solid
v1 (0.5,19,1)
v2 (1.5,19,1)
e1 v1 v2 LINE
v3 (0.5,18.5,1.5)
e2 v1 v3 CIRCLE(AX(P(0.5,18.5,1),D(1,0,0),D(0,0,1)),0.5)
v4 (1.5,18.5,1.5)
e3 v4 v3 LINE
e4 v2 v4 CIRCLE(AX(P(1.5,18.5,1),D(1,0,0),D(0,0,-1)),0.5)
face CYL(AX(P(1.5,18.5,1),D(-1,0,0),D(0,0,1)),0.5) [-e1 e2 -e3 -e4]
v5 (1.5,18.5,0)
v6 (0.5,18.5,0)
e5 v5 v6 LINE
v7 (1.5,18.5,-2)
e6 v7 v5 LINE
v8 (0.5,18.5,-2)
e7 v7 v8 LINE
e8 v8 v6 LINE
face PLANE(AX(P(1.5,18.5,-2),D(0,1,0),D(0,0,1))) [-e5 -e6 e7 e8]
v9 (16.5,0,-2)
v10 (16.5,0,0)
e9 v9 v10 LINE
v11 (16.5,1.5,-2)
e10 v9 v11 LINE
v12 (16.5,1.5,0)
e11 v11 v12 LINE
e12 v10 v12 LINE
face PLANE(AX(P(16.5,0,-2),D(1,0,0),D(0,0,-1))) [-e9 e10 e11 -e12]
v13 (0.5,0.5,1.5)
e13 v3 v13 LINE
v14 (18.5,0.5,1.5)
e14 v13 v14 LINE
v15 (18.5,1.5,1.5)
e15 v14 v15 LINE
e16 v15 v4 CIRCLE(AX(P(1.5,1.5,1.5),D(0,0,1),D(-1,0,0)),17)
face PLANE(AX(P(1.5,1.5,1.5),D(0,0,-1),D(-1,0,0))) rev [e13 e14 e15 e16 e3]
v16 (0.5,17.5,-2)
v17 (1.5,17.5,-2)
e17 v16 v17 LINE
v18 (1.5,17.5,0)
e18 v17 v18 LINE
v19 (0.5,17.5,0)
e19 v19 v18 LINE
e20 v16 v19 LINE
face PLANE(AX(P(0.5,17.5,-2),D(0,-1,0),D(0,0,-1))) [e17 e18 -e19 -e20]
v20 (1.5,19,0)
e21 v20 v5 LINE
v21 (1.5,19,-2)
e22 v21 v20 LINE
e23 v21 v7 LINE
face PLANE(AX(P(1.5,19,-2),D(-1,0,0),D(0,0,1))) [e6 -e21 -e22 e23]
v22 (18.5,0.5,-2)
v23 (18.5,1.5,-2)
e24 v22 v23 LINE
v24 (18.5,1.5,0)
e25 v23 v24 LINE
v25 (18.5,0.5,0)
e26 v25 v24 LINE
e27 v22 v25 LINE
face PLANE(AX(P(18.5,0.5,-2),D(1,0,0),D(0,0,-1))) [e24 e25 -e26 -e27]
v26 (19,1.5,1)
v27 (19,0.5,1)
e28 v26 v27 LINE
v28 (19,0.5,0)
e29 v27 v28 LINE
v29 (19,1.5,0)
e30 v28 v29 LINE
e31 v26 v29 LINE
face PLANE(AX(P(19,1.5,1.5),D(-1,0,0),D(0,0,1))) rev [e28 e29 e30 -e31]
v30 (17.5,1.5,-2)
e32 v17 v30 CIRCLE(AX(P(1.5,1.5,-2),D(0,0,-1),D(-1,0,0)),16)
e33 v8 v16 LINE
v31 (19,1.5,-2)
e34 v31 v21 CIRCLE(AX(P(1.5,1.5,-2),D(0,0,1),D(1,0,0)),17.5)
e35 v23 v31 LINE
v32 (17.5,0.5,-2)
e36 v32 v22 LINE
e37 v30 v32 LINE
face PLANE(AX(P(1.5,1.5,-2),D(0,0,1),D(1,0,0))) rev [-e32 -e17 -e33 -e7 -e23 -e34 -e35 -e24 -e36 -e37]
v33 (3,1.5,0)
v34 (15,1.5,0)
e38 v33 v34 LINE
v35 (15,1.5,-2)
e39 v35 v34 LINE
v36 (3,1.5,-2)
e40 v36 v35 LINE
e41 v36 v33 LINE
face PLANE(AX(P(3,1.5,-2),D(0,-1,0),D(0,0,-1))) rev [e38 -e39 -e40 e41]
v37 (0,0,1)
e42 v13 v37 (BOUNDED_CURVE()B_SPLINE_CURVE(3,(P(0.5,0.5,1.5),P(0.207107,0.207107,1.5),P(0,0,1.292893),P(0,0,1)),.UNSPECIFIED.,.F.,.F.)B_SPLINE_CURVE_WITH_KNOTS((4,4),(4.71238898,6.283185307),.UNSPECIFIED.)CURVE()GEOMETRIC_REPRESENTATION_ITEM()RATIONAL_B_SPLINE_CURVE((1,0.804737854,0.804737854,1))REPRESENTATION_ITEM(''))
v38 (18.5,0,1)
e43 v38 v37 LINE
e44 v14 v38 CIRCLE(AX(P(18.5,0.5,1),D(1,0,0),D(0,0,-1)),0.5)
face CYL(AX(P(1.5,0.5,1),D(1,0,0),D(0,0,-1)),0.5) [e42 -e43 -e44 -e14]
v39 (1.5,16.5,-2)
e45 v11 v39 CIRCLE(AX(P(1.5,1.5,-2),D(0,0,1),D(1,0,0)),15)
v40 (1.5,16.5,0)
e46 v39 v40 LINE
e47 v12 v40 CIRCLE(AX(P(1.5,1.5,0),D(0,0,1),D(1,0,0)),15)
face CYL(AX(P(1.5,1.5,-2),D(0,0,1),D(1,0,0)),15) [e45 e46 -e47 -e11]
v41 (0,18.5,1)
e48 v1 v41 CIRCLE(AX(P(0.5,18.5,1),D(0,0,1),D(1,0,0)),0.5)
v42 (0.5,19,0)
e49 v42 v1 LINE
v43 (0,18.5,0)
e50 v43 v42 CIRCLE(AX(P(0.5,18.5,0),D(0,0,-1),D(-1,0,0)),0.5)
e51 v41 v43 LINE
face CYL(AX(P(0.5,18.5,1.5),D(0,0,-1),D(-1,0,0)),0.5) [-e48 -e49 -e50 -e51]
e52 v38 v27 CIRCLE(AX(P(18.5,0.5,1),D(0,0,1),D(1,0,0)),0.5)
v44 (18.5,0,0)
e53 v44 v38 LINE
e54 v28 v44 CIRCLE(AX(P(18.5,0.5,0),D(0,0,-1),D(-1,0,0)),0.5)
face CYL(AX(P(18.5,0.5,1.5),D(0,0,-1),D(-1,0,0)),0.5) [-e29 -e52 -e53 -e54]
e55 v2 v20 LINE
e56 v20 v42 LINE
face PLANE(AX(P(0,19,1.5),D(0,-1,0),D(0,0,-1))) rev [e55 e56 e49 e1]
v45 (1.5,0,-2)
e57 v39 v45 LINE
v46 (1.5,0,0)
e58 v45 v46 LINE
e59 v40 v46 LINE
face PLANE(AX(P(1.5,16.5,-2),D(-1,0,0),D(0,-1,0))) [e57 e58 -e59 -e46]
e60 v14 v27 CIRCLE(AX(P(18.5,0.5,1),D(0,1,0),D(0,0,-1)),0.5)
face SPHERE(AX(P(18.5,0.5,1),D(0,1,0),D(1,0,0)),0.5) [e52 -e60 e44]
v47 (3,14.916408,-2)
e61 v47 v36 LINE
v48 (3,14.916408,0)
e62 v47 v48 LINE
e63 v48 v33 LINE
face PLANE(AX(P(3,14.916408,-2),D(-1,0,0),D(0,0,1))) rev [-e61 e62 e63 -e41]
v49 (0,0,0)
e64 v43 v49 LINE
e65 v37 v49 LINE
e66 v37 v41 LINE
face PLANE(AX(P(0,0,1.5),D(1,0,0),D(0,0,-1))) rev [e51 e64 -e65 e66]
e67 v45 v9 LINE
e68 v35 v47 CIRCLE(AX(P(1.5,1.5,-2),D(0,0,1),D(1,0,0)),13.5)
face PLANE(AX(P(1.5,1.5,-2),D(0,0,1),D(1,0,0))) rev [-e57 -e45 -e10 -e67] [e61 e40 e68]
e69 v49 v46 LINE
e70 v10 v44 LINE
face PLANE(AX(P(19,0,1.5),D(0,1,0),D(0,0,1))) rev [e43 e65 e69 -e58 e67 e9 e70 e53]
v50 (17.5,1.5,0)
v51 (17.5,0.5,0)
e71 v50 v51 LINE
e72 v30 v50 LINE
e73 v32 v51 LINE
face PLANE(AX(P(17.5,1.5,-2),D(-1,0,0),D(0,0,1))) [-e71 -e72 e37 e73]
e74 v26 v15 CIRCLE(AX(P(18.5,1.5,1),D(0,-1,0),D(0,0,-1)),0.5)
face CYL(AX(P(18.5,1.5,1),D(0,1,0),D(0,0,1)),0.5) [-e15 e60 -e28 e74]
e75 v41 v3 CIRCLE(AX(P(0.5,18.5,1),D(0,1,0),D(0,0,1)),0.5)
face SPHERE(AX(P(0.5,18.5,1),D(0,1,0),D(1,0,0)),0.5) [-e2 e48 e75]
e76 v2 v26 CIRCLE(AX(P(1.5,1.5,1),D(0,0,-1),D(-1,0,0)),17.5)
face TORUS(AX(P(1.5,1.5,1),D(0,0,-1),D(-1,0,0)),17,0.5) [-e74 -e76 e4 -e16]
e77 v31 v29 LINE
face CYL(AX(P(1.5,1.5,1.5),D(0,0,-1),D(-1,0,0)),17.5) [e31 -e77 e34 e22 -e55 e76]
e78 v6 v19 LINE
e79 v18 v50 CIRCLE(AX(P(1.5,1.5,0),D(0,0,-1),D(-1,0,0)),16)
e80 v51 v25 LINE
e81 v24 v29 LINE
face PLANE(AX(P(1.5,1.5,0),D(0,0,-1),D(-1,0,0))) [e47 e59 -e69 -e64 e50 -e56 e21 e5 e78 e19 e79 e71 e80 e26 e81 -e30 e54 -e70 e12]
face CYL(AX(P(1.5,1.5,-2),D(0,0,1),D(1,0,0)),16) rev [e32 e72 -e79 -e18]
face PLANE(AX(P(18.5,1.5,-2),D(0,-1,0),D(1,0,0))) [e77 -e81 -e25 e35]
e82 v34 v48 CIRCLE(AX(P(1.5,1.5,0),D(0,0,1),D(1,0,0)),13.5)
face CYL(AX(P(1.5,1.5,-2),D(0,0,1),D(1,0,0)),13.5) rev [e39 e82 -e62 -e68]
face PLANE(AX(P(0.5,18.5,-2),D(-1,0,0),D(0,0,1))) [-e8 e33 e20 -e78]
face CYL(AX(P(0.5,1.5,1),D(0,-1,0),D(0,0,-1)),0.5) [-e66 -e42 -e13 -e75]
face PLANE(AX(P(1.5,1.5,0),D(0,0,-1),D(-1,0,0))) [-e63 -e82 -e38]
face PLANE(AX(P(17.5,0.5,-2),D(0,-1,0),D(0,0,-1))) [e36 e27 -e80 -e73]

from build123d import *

# Parameters (mm, degrees)
BOSS_EXTRUDE1_DEPTH = 1.5
BOSS_EXTRUDE3_START = -2
BOSS_EXTRUDE3_DEPTH = 2
FILETE1_R           = 0.5


with BuildPart() as part:
    # Sketch1 → Boss-Extrude1 (new body)
    with BuildSketch(Plane.XY):
        with BuildLine():
            Line((0, 0), (0, 19))
            Line((0, 19), (1.5, 19))
            ThreePointArc((1.5, 19), (13.874368671, 13.874368671), (19, 1.5))
            Line((19, 1.5), (19, 0))
            Line((19, 0), (0, 0))
        make_face()
    extrude(amount=BOSS_EXTRUDE1_DEPTH)

    # Sketch2 → Boss-Extrude3 (add)
    # profile 1 of 2: a face of its own
    with BuildSketch(Plane.XY.offset(BOSS_EXTRUDE3_START)):
        with BuildLine():
            Line((1.5, 19), (1.5, 18.5))
            Line((1.5, 18.5), (0.5, 18.5))
            Line((0.5, 18.5), (0.5, 17.5))
            Line((0.5, 17.5), (1.5, 17.5))
            ThreePointArc((1.5, 17.5), (12.813708499, 12.813708499), (17.5, 1.5))
            Line((17.5, 1.5), (17.5, 0.5))
            Line((17.5, 0.5), (18.5, 0.5))
            Line((18.5, 0.5), (18.5, 1.5))
            Line((18.5, 1.5), (19, 1.5))
            ThreePointArc((19, 1.5), (13.874368671, 13.874368671), (1.5, 19))
        make_face()
    # profile 2 of 2: a face of its own
    with BuildSketch(Plane.XY.offset(BOSS_EXTRUDE3_START)):
        with BuildLine():
            Line((1.5, 16.5), (1.5, 0))
            Line((1.5, 0), (16.5, 0))
            Line((16.5, 0), (16.5, 1.5))
            ThreePointArc((16.5, 1.5), (12.106601718, 12.106601718), (1.5, 16.5))
        make_face()
        with BuildLine():
            Line((3, 14.916407865), (3, 1.5))
            Line((3, 1.5), (15, 1.5))
            ThreePointArc((15, 1.5), (11.562305899, 10.5), (3, 14.916407865))
        make_face(mode=Mode.SUBTRACT)
    extrude(amount=BOSS_EXTRUDE3_DEPTH)

    # Filete1
    filete1_edges = [part.edges().sort_by_distance(p)[0] for p in [
        (13.874368671, 13.874368671, 1.5),
        (0.75, 19, 1.5),
        (0, 9.5, 1.5),
        (9.5, 0, 1.5),
        (19, 0.75, 1.5),
        (0, 19, 0.75),
        (19, 0, 0.75),
    ]]
    fillet(filete1_edges, radius=FILETE1_R)


solid = part.part
